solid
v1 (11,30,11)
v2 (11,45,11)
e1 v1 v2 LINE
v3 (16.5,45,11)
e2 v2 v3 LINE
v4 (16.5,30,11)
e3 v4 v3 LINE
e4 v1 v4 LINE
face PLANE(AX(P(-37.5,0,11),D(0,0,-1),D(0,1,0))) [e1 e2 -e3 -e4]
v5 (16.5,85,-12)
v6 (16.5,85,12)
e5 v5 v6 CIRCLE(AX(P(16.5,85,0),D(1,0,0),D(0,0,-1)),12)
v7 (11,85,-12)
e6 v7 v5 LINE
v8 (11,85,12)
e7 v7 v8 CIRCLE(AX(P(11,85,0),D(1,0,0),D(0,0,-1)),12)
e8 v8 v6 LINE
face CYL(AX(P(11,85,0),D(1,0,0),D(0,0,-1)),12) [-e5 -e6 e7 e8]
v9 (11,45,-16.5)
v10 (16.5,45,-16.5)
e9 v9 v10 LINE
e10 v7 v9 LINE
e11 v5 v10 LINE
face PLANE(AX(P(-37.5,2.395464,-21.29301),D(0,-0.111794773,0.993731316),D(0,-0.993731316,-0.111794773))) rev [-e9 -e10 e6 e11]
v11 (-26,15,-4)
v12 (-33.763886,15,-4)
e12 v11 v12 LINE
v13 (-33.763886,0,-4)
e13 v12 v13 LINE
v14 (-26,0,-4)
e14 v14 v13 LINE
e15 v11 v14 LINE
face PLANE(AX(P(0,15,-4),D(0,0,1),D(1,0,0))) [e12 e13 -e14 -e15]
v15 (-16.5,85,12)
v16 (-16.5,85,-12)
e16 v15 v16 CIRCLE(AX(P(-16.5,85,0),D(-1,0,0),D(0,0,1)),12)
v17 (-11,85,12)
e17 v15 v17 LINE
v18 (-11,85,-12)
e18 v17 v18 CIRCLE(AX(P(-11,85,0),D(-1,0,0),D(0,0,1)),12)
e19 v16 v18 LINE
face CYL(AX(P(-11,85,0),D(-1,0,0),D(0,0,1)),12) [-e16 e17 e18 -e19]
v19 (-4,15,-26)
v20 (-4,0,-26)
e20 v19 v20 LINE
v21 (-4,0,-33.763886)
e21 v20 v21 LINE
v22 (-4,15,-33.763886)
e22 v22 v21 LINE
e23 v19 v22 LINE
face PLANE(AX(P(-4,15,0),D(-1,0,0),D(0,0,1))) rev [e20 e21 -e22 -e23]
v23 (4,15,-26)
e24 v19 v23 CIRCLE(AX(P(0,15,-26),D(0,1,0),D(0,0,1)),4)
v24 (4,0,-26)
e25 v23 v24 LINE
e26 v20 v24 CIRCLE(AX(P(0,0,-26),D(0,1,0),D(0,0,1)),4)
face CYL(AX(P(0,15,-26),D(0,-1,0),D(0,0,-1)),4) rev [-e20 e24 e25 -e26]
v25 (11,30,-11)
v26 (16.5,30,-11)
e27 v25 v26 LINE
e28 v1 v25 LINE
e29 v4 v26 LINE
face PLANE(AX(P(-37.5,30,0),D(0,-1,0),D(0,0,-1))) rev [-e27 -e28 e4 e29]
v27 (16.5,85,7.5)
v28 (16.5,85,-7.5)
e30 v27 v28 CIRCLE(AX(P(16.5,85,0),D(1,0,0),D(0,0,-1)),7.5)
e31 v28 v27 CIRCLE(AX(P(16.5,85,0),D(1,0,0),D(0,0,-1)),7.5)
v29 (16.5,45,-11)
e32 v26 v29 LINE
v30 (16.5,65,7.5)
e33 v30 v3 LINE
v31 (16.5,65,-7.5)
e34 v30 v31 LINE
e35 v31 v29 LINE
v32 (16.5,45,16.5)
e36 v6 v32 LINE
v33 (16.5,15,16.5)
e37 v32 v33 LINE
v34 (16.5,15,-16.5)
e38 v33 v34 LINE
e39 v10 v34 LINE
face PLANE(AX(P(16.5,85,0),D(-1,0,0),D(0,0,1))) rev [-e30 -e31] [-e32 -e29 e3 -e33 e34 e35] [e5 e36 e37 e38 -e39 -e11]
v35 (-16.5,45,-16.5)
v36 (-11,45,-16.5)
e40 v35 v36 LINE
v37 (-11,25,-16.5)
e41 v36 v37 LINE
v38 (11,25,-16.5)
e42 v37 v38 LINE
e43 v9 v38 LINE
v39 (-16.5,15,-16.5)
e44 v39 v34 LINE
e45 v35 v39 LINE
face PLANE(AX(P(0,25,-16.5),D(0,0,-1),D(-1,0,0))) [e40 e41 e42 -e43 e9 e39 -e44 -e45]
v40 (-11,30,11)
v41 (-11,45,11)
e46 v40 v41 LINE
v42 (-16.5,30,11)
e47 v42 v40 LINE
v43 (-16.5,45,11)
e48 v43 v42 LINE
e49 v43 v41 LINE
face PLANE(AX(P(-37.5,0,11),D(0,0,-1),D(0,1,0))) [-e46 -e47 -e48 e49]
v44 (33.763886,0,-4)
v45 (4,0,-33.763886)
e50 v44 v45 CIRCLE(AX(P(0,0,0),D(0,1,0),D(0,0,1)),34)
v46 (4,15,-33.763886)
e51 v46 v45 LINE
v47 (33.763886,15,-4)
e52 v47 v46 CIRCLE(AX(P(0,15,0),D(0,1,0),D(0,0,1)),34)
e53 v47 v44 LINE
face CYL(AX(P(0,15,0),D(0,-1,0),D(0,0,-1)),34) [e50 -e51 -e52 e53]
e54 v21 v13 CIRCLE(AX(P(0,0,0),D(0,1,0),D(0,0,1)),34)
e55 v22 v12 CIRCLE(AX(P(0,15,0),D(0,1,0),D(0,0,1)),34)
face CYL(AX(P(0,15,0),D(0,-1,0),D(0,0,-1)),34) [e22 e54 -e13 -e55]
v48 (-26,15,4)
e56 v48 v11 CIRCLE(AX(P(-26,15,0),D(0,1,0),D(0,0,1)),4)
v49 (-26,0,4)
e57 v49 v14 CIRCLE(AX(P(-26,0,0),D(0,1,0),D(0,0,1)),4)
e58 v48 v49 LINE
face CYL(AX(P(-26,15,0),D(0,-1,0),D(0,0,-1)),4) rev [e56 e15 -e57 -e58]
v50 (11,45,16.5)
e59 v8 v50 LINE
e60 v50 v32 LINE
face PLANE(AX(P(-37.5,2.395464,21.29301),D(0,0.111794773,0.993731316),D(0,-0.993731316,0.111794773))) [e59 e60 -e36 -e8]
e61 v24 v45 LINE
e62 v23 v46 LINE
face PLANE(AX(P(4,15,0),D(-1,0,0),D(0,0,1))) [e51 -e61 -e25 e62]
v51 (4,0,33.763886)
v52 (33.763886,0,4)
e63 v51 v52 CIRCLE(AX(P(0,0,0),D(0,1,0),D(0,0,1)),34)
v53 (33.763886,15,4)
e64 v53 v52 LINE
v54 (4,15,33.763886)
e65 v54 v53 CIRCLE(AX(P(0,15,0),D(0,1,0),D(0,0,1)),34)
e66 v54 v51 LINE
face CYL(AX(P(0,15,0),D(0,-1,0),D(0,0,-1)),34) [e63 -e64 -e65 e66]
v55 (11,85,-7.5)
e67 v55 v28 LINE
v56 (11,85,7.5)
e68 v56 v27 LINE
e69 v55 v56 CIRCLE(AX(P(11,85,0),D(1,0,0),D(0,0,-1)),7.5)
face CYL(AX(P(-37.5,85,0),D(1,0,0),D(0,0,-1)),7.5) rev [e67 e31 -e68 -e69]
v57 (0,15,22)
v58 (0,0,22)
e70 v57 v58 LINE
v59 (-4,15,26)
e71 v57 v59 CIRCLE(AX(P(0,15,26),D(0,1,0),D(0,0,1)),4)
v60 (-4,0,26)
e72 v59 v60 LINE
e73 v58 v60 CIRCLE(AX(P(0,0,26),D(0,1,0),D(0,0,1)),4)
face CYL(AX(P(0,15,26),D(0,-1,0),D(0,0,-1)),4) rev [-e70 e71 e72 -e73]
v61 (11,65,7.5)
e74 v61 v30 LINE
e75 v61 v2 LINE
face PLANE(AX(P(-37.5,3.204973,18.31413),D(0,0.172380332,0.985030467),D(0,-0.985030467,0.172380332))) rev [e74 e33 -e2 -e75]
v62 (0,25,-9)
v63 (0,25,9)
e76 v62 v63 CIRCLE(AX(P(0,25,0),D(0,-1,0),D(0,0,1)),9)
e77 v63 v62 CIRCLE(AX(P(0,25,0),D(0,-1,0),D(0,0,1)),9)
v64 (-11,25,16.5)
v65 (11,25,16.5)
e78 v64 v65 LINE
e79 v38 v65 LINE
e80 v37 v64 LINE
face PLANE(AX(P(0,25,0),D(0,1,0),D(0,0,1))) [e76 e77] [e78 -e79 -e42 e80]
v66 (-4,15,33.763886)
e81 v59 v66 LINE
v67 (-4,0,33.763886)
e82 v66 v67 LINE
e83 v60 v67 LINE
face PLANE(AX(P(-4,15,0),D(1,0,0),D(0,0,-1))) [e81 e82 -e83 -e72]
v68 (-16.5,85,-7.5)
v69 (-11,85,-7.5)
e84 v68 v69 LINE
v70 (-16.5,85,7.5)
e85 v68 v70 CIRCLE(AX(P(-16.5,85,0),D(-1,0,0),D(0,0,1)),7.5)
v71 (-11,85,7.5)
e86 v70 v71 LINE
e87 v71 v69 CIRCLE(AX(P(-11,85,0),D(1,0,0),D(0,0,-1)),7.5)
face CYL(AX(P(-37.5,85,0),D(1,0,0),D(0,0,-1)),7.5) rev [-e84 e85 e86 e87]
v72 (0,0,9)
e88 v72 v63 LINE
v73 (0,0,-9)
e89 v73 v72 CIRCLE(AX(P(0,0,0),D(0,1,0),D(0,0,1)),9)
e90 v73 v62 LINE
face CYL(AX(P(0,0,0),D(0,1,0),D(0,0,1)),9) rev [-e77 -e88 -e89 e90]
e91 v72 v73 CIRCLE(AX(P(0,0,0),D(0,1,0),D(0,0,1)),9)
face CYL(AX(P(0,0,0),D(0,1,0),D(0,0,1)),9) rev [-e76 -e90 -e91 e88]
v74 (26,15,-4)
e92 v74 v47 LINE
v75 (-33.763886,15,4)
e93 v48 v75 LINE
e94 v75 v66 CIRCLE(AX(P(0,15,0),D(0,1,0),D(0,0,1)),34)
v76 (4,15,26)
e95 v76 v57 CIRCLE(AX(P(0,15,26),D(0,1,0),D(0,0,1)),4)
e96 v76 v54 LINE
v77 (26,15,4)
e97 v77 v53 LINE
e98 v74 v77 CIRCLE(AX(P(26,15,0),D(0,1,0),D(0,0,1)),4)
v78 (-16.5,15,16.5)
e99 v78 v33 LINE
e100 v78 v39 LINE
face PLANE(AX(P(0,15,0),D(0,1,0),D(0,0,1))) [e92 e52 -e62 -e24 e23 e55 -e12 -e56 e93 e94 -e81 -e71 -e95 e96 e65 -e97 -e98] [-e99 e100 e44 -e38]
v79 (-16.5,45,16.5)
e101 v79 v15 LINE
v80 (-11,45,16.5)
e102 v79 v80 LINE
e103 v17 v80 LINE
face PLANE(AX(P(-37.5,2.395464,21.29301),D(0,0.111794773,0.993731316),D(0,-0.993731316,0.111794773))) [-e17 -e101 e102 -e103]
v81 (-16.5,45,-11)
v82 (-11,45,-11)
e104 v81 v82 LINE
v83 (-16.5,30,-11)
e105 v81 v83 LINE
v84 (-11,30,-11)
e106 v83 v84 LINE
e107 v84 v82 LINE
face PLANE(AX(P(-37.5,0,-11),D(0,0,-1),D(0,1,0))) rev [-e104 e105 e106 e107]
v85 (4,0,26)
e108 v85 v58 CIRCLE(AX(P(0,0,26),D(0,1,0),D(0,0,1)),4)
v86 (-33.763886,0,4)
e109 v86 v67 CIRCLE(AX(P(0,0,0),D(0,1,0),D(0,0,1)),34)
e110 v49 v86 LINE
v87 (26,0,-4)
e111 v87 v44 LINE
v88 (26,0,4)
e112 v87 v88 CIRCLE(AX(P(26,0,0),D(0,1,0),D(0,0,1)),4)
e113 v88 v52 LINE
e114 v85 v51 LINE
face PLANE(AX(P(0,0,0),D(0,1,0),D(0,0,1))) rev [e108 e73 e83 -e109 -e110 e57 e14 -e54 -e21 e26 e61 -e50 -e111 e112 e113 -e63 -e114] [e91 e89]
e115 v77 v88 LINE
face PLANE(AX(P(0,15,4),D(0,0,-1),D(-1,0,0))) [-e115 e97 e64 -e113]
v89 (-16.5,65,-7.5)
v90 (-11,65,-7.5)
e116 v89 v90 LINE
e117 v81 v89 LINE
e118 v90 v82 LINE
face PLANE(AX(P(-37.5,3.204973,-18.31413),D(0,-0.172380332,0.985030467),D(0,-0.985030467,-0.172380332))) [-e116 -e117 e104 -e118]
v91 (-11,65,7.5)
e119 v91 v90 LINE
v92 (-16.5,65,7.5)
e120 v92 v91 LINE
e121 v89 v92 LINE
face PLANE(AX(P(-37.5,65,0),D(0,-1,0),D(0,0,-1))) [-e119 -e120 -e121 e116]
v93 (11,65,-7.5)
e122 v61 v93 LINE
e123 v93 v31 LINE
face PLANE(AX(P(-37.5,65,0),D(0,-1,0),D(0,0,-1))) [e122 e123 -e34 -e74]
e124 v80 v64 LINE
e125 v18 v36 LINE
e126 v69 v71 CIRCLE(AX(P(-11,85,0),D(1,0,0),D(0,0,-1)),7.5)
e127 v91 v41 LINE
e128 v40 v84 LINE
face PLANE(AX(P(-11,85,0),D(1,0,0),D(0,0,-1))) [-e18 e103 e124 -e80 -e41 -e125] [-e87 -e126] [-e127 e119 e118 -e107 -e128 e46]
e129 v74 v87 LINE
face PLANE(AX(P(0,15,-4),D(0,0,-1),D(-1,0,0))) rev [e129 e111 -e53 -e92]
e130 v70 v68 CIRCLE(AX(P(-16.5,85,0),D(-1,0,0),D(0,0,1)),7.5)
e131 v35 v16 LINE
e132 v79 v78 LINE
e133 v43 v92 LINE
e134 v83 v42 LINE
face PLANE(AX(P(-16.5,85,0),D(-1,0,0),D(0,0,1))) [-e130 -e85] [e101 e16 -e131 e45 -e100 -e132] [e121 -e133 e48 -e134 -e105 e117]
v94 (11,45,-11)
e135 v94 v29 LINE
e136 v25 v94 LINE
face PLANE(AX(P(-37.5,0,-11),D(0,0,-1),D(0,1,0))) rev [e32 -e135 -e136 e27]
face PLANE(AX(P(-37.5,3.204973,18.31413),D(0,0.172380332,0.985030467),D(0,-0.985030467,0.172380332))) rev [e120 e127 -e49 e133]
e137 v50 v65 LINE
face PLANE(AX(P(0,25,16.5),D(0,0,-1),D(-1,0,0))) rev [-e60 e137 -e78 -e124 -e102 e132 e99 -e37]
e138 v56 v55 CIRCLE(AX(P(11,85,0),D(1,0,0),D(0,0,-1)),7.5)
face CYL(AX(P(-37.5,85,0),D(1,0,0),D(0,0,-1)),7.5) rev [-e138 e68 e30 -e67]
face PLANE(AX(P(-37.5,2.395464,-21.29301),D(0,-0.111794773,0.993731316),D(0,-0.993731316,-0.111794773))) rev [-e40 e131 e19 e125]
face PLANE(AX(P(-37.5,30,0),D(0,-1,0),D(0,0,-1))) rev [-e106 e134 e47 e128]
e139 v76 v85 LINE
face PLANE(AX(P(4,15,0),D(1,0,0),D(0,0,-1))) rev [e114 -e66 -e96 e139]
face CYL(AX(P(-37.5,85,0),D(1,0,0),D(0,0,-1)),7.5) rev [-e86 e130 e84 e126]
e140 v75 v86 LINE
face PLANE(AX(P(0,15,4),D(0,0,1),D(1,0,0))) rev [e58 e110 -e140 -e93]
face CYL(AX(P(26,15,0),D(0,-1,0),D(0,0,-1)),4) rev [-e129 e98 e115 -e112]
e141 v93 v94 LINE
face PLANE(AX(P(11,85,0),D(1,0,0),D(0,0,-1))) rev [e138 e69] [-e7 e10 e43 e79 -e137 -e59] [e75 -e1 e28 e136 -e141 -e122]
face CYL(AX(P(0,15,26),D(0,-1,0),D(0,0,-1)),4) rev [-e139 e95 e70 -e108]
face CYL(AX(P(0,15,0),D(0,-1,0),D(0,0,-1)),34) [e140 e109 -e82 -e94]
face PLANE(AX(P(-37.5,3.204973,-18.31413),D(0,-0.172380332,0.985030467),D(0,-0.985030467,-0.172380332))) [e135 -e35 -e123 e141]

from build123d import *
from build123d.topology import SkipClean

# Parameters (mm, degrees)
BASE_FLANGE_DEPTH       = 15
CENTRE_HOLE_SKETCH_R    = 9
CENTRE_HOLE_18_DEPTH    = 15
LUG_START               = 10
LUG_BASE_PAD_DEPTH      = 10
CLEVIS_LUG_BLOCKS_DEPTH = 70
LUG_PROFILE_CUT_DEPTH   = 54
LUG_EYE_BOSS_DEPTH      = 5.5
LUG_START_2             = -5.5
LUG_WEB_DEPTH           = 5.5


with BuildPart() as part:
    # Base Flange Sketch → Base Flange (new body)
    with BuildSketch(Plane(origin=(0, 0, 0), x_dir=(1, 0, 0), z_dir=(0, 1, 0))):
        with BuildLine():
            ThreePointArc((26, -4), (25.846039759, -3.997035932), (25.692307692, -3.988148122))
            ThreePointArc((25.692307692, -3.988148122), (18.384776311, -18.384776311), (3.988148122, -25.692307692))
            ThreePointArc((3.988148122, -25.692307692), (3.997035932, -25.846039759), (4, -26))
            Line((4, -26), (4, -33.763886032))
            ThreePointArc((4, -33.763886032), (24.04163056, -24.04163056), (33.763886032, -4))
            Line((33.763886032, -4), (26, -4))
        make_face()
        with BuildLine():
            ThreePointArc((25.692307692, 3.988148122), (25.846039759, 3.997035932), (26, 4))
            Line((26, 4), (33.763886032, 4))
            ThreePointArc((33.763886032, 4), (24.04163056, 24.04163056), (4, 33.763886032))
            Line((4, 33.763886032), (4, 26))
            ThreePointArc((4, 26), (3.997035932, 25.846039759), (3.988148122, 25.692307692))
            ThreePointArc((3.988148122, 25.692307692), (18.384776311, 18.384776311), (25.692307692, 3.988148122))
        make_face()
        with BuildLine():
            ThreePointArc((-25.692307692, 3.988148122), (-18.384776311, 18.384776311), (-3.988148122, 25.692307692))
            ThreePointArc((-3.988148122, 25.692307692), (-3.997035932, 25.846039759), (-4, 26))
            Line((-4, 26), (-4, 33.763886032))
            ThreePointArc((-4, 33.763886032), (-24.04163056, 24.04163056), (-33.763886032, 4))
            Line((-33.763886032, 4), (-26, 4))
            ThreePointArc((-26, 4), (-25.846039759, 3.997035932), (-25.692307692, 3.988148122))
        make_face()
        with BuildLine():
            ThreePointArc((-4, -26), (-3.997035932, -25.846039759), (-3.988148122, -25.692307692))
            ThreePointArc((-3.988148122, -25.692307692), (-18.384776311, -18.384776311), (-25.692307692, -3.988148122))
            ThreePointArc((-25.692307692, -3.988148122), (-25.846039759, -3.997035932), (-26, -4))
            Line((-26, -4), (-33.763886032, -4))
            ThreePointArc((-33.763886032, -4), (-24.04163056, -24.04163056), (-4, -33.763886032))
            Line((-4, -33.763886032), (-4, -26))
        make_face()
        with BuildLine():
            ThreePointArc((25.692307692, -3.988148122), (22, 0), (25.692307692, 3.988148122))
            ThreePointArc((25.692307692, 3.988148122), (18.384776311, 18.384776311), (3.988148122, 25.692307692))
            ThreePointArc((3.988148122, 25.692307692), (0, 22), (-3.988148122, 25.692307692))
            ThreePointArc((-3.988148122, 25.692307692), (-18.384776311, 18.384776311), (-25.692307692, 3.988148122))
            ThreePointArc((-25.692307692, 3.988148122), (-22, 0), (-25.692307692, -3.988148122))
            ThreePointArc((-25.692307692, -3.988148122), (-18.384776311, -18.384776311), (-3.988148122, -25.692307692))
            ThreePointArc((-3.988148122, -25.692307692), (0, -22), (3.988148122, -25.692307692))
            ThreePointArc((3.988148122, -25.692307692), (18.384776311, -18.384776311), (25.692307692, -3.988148122))
        make_face()
    extrude(amount=BASE_FLANGE_DEPTH)

    # Centre Hole Sketch → Centre Hole _18 (cut)
    with BuildSketch(Plane(origin=(0, 15, 0), x_dir=(1, 0, 0), z_dir=(0, 1, 0))):
        with Locations(Location((0, 0, 0), (0, 0, 270))):
            Circle(CENTRE_HOLE_SKETCH_R)
    extrude(amount=-CENTRE_HOLE_18_DEPTH, mode=Mode.SUBTRACT)

    # Lug Base Sketch → Lug Base Pad (add)
    with BuildSketch(Plane(origin=(0, 15, 0), x_dir=(1, 0, 0), z_dir=(0, 1, 0)).offset(LUG_START)):
        Polygon((11, -11), (0, -11), (-11, -11), (-11, -16.5), (11, -16.5), align=None)
        Polygon((0, 11), (11, 11), (11, 16.5), (-11, 16.5), (-11, 11), align=None)
        with BuildLine():
            Line((0, -9), (0, -11))
            Line((0, -11), (11, -11))
            Line((11, -11), (11, 11))
            Line((11, 11), (0, 11))
            Line((0, 11), (0, 9))
            ThreePointArc((0, 9), (6.363961031, 6.363961031), (9, 0))
            ThreePointArc((9, 0), (6.363961031, -6.363961031), (0, -9))
        make_face()
        with BuildLine():
            Line((-11, -11), (0, -11))
            Line((0, -11), (0, -9))
            ThreePointArc((0, -9), (-9, 0), (0, 9))
            Line((0, 9), (0, 11))
            Line((0, 11), (-11, 11))
            Line((-11, 11), (-11, -11))
        make_face()
    extrude(amount=-LUG_BASE_PAD_DEPTH)

    # Sketch3_3 → Clevis Lug Blocks (add)
    with BuildSketch(Plane(origin=(0, 15, 0), x_dir=(1, 0, 0), z_dir=(0, 1, 0))):
        Polygon((11, 11), (11, -11), (11, -16.5), (16.5, -16.5), (16.5, 16.5), (11, 16.5), align=None)
        Polygon((-11, -16.5), (-11, -11), (-11, 11), (-11, 16.5), (-16.5, 16.5), (-16.5, -16.5), align=None)
    extrude(amount=CLEVIS_LUG_BLOCKS_DEPTH)

    # Lug Profile Sketch → Lug Profile Cut (cut)
    with BuildSketch(Plane(origin=(16.5, 0, 0), x_dir=(0, 0, -1), z_dir=(1, 0, 0))):
        Polygon((16.5, 85), (12, 85), (16.5, 45), align=None)
        Polygon((-16.5, 45), (-12, 85), (-16.5, 85), align=None)
        Polygon((-11, 30), (-11, 45), (-7.5, 65), (0, 65), (7.5, 65), (11, 45), (11, 30), align=None)
        with BuildLine():
            Line((7.5, 85), (-7.5, 85))
            ThreePointArc((-7.5, 85), (0, 77.5), (7.5, 85))
        make_face()
        with BuildLine():
            ThreePointArc((7.5, 85), (0, 92.5), (-7.5, 85))
            Line((-7.5, 85), (7.5, 85))
        make_face()
    extrude(amount=-LUG_PROFILE_CUT_DEPTH, mode=Mode.SUBTRACT)

    # Sketch6_4 → Lug Eye Boss (add)
    with SkipClean():  # the faces are left unmerged after this step: merging them gives an invalid solid
        with BuildSketch(Plane(origin=(16.5, 0, 0), x_dir=(0, 0, -1), z_dir=(1, 0, 0))):
            with BuildLine():
                Line((-7.5, 85), (-12, 85))
                ThreePointArc((-12, 85), (0, 73), (12, 85))
                Line((12, 85), (7.5, 85))
                ThreePointArc((7.5, 85), (0, 77.5), (-7.5, 85))
            make_face()
            with BuildLine():
                ThreePointArc((12, 85), (0, 97), (-12, 85))
                Line((-12, 85), (-7.5, 85))
                ThreePointArc((-7.5, 85), (0, 92.5), (7.5, 85))
                Line((7.5, 85), (12, 85))
            make_face()
        extrude(amount=-LUG_EYE_BOSS_DEPTH)

    # Lug Web Sketch → Lug Web (add)
    with SkipClean():  # the faces are left unmerged after this step: merging them gives an invalid solid
        with BuildSketch(Plane.ZY.offset(16.5).offset(LUG_START_2)):
            with BuildLine():
                Line((7.5, 85), (12, 85))
                ThreePointArc((12, 85), (0, 97), (-12, 85))
                Line((-12, 85), (-7.5, 85))
                ThreePointArc((-7.5, 85), (0, 92.5), (7.5, 85))
            make_face()
        extrude(amount=LUG_WEB_DEPTH)


solid = part.part
